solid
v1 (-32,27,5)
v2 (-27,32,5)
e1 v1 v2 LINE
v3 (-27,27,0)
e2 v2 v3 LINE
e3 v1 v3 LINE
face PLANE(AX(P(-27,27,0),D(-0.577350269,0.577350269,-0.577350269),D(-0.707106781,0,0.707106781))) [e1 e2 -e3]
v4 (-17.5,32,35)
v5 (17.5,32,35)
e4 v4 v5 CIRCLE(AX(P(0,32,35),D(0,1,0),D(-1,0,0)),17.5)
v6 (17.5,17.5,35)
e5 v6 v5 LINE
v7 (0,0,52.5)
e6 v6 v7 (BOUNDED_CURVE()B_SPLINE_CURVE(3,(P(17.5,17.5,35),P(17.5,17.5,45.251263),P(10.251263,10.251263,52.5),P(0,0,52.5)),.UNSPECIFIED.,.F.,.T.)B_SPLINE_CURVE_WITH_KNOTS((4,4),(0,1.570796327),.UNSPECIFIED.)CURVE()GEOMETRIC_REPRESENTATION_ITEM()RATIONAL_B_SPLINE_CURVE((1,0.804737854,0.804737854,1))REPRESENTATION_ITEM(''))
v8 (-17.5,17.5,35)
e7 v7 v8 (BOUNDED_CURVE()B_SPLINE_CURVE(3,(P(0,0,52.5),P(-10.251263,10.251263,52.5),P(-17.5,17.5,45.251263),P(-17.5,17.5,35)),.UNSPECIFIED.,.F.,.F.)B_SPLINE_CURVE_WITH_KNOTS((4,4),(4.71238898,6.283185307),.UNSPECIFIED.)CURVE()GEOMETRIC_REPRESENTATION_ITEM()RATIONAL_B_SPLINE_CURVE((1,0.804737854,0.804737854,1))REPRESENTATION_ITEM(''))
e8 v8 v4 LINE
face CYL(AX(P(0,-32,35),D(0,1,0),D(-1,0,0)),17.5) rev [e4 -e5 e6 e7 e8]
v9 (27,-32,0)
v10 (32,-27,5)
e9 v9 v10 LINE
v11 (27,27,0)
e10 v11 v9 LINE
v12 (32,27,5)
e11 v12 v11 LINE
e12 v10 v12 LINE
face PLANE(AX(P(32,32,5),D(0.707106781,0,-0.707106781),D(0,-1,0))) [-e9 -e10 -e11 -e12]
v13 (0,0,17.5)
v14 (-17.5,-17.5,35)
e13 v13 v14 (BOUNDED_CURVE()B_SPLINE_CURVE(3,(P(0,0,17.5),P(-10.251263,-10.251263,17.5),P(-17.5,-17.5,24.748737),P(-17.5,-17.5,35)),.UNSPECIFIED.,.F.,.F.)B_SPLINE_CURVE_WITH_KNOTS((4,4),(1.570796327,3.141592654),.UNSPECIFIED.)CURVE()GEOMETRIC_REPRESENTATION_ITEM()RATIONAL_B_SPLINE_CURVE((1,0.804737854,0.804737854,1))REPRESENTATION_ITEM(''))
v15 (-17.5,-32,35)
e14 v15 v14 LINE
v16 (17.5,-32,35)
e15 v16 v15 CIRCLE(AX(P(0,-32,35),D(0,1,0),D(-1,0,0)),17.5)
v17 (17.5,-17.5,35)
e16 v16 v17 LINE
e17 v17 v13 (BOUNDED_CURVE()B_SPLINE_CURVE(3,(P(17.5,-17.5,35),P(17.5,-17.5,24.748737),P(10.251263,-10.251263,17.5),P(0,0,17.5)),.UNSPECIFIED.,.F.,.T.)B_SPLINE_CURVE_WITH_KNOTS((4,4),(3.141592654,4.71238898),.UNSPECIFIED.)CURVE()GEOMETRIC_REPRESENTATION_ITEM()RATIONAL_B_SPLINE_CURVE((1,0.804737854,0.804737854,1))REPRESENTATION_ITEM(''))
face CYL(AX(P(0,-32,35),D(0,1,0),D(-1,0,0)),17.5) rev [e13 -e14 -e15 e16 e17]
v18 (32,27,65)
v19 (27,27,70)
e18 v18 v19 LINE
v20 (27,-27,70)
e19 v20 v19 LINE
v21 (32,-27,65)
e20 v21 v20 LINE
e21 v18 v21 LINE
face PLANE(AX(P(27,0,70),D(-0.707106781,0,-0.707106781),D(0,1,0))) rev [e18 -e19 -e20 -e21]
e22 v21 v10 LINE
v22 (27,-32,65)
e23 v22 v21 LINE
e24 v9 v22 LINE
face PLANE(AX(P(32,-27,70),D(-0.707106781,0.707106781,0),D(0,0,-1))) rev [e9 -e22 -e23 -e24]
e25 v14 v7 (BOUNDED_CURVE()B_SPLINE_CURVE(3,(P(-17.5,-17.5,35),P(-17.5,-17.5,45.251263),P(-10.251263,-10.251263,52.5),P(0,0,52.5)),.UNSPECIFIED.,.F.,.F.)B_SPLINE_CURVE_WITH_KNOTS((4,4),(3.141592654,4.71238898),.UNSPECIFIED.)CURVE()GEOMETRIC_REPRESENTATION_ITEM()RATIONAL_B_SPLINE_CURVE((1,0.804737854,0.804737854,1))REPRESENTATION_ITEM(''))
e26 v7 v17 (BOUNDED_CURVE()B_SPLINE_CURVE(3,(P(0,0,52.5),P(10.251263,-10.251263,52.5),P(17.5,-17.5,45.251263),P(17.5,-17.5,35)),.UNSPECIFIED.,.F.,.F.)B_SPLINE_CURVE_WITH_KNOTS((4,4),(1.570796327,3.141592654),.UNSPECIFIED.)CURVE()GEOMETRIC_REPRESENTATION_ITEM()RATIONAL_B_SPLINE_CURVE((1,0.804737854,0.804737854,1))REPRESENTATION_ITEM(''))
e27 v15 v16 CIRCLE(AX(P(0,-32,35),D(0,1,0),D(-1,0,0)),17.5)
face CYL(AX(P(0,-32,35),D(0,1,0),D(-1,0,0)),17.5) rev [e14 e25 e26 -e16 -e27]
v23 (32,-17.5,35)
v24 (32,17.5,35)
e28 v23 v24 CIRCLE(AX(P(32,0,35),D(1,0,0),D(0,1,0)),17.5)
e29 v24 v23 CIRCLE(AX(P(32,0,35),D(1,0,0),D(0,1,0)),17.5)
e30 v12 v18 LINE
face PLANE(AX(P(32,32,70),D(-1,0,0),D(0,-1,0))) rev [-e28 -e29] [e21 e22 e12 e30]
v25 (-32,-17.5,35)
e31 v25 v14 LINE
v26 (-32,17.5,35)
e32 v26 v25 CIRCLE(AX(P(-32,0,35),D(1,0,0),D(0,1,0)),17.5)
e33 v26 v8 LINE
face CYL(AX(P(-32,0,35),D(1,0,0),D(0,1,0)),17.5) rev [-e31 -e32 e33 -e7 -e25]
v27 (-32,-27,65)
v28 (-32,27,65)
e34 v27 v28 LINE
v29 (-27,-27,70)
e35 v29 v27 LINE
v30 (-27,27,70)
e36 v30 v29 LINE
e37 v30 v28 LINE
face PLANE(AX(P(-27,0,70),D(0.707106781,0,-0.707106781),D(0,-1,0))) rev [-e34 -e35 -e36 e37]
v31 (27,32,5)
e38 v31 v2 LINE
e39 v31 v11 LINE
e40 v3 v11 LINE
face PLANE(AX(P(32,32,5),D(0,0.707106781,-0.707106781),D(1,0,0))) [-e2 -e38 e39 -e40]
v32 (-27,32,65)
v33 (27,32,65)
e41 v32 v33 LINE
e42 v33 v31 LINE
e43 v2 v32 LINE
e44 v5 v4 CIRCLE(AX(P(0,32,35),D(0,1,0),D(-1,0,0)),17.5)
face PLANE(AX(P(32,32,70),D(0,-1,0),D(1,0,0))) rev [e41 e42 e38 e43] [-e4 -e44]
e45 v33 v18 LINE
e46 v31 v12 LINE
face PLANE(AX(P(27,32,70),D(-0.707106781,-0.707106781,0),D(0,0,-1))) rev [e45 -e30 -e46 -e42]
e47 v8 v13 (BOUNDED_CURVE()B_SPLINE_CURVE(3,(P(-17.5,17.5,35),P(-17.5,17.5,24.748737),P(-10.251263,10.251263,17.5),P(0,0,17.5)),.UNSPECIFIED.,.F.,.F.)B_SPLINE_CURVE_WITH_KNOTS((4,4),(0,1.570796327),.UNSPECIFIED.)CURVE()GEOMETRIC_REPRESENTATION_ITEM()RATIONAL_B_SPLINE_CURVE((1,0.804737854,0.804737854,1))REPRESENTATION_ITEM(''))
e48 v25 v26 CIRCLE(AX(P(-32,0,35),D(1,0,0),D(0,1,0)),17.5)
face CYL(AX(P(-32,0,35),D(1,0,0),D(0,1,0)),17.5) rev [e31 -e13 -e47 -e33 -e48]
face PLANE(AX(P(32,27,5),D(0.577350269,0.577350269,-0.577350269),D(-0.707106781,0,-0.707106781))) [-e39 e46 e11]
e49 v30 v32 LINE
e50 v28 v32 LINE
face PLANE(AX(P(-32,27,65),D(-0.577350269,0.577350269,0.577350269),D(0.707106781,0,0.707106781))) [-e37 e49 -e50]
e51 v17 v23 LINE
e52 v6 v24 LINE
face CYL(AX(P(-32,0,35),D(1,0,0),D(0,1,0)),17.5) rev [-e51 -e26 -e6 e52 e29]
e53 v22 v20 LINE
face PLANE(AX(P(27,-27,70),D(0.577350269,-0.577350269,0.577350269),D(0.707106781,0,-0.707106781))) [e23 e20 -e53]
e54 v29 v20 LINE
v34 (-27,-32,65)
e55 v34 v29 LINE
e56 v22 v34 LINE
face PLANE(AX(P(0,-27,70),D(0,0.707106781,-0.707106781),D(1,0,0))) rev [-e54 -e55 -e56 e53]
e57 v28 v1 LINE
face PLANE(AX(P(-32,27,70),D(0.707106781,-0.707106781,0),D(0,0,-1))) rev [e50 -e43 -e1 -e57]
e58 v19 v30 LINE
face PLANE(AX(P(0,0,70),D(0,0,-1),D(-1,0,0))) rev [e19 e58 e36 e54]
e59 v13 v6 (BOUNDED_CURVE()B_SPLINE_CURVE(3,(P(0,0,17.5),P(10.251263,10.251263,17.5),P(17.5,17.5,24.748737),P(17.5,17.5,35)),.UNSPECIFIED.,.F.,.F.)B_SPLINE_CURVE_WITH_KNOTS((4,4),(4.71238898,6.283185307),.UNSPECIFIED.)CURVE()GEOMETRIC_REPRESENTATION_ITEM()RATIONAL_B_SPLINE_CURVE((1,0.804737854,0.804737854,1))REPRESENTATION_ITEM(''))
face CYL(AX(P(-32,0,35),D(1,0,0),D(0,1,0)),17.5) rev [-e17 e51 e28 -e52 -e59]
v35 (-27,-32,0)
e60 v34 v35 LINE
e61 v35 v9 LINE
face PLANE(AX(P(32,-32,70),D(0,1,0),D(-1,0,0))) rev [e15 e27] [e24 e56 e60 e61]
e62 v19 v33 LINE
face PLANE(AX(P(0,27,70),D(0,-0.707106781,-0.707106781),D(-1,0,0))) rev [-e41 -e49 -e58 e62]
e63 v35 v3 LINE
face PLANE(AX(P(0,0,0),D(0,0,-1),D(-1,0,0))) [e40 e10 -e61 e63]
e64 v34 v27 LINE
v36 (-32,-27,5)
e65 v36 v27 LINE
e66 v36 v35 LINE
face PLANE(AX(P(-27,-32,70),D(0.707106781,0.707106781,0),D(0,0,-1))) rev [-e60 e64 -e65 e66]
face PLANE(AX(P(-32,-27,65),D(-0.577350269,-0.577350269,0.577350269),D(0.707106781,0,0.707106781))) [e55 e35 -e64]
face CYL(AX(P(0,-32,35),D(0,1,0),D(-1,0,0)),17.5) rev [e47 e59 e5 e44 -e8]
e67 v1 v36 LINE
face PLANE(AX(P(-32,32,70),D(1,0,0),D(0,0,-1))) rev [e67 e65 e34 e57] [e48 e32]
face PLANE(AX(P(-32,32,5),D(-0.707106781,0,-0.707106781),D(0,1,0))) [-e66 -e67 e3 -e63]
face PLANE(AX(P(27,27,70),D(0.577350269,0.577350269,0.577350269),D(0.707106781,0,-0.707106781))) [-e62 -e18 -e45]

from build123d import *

# Parameters (mm, degrees)
BLOCK_PROFILE_SKETCH_W  = 64
BLOCK_PROFILE_SKETCH_H  = 64
BLOCK_BODY_DEPTH        = 70
CROSS_HOLE_A_SKETCH_R   = 17.5
CROSS_HOLE_A_DEPTH      = 101.09995005
CROSS_HOLE_B_SKETCH_R   = 17.5
CROSS_HOLE_B_DEPTH      = 101.09995005
EDGE_CHAMFERS_5X45_SIZE = 5


with BuildPart() as part:
    # Block Profile Sketch → Block Body (new body)
    with BuildSketch(Plane.XY):
        Rectangle(BLOCK_PROFILE_SKETCH_W, BLOCK_PROFILE_SKETCH_H)
    extrude(amount=BLOCK_BODY_DEPTH)

    # Cross Hole A Sketch → Cross Hole A (cut, through all)
    with BuildSketch(Plane(origin=(0, 32, 0), x_dir=(1, 0, 0), z_dir=(0, 1, 0))):
        with Locations(Location((0, -35, 0), (0, 0, 180))):
            Circle(CROSS_HOLE_A_SKETCH_R)
    extrude(amount=-CROSS_HOLE_A_DEPTH, mode=Mode.SUBTRACT)

    # Cross Hole B Sketch → Cross Hole B (cut, through all)
    with BuildSketch(Plane(origin=(32, 0, 0), x_dir=(0, 0, -1), z_dir=(1, 0, 0))):
        with Locations(Location((-35, 0, 0), (0, 0, 90))):
            Circle(CROSS_HOLE_B_SKETCH_R)
    extrude(amount=-CROSS_HOLE_B_DEPTH, mode=Mode.SUBTRACT)

    # Edge Chamfers 5x45°
    edge_chamfers_5x45_edges = [part.edges().sort_by_distance(p)[0] for p in [
        (32, 0, 70),
        (0, 32, 70),
        (-32, 0, 70),
        (0, 32, 0),
        (32, 0, 0),
        (-32, 0, 0),
        (-32, 32, 35),
        (32, 32, 35),
        (32, -32, 35),
        (-32, -32, 35),
        (0, -32, 70),
    ]]
    chamfer(edge_chamfers_5x45_edges, length=EDGE_CHAMFERS_5X45_SIZE)


solid = part.part
